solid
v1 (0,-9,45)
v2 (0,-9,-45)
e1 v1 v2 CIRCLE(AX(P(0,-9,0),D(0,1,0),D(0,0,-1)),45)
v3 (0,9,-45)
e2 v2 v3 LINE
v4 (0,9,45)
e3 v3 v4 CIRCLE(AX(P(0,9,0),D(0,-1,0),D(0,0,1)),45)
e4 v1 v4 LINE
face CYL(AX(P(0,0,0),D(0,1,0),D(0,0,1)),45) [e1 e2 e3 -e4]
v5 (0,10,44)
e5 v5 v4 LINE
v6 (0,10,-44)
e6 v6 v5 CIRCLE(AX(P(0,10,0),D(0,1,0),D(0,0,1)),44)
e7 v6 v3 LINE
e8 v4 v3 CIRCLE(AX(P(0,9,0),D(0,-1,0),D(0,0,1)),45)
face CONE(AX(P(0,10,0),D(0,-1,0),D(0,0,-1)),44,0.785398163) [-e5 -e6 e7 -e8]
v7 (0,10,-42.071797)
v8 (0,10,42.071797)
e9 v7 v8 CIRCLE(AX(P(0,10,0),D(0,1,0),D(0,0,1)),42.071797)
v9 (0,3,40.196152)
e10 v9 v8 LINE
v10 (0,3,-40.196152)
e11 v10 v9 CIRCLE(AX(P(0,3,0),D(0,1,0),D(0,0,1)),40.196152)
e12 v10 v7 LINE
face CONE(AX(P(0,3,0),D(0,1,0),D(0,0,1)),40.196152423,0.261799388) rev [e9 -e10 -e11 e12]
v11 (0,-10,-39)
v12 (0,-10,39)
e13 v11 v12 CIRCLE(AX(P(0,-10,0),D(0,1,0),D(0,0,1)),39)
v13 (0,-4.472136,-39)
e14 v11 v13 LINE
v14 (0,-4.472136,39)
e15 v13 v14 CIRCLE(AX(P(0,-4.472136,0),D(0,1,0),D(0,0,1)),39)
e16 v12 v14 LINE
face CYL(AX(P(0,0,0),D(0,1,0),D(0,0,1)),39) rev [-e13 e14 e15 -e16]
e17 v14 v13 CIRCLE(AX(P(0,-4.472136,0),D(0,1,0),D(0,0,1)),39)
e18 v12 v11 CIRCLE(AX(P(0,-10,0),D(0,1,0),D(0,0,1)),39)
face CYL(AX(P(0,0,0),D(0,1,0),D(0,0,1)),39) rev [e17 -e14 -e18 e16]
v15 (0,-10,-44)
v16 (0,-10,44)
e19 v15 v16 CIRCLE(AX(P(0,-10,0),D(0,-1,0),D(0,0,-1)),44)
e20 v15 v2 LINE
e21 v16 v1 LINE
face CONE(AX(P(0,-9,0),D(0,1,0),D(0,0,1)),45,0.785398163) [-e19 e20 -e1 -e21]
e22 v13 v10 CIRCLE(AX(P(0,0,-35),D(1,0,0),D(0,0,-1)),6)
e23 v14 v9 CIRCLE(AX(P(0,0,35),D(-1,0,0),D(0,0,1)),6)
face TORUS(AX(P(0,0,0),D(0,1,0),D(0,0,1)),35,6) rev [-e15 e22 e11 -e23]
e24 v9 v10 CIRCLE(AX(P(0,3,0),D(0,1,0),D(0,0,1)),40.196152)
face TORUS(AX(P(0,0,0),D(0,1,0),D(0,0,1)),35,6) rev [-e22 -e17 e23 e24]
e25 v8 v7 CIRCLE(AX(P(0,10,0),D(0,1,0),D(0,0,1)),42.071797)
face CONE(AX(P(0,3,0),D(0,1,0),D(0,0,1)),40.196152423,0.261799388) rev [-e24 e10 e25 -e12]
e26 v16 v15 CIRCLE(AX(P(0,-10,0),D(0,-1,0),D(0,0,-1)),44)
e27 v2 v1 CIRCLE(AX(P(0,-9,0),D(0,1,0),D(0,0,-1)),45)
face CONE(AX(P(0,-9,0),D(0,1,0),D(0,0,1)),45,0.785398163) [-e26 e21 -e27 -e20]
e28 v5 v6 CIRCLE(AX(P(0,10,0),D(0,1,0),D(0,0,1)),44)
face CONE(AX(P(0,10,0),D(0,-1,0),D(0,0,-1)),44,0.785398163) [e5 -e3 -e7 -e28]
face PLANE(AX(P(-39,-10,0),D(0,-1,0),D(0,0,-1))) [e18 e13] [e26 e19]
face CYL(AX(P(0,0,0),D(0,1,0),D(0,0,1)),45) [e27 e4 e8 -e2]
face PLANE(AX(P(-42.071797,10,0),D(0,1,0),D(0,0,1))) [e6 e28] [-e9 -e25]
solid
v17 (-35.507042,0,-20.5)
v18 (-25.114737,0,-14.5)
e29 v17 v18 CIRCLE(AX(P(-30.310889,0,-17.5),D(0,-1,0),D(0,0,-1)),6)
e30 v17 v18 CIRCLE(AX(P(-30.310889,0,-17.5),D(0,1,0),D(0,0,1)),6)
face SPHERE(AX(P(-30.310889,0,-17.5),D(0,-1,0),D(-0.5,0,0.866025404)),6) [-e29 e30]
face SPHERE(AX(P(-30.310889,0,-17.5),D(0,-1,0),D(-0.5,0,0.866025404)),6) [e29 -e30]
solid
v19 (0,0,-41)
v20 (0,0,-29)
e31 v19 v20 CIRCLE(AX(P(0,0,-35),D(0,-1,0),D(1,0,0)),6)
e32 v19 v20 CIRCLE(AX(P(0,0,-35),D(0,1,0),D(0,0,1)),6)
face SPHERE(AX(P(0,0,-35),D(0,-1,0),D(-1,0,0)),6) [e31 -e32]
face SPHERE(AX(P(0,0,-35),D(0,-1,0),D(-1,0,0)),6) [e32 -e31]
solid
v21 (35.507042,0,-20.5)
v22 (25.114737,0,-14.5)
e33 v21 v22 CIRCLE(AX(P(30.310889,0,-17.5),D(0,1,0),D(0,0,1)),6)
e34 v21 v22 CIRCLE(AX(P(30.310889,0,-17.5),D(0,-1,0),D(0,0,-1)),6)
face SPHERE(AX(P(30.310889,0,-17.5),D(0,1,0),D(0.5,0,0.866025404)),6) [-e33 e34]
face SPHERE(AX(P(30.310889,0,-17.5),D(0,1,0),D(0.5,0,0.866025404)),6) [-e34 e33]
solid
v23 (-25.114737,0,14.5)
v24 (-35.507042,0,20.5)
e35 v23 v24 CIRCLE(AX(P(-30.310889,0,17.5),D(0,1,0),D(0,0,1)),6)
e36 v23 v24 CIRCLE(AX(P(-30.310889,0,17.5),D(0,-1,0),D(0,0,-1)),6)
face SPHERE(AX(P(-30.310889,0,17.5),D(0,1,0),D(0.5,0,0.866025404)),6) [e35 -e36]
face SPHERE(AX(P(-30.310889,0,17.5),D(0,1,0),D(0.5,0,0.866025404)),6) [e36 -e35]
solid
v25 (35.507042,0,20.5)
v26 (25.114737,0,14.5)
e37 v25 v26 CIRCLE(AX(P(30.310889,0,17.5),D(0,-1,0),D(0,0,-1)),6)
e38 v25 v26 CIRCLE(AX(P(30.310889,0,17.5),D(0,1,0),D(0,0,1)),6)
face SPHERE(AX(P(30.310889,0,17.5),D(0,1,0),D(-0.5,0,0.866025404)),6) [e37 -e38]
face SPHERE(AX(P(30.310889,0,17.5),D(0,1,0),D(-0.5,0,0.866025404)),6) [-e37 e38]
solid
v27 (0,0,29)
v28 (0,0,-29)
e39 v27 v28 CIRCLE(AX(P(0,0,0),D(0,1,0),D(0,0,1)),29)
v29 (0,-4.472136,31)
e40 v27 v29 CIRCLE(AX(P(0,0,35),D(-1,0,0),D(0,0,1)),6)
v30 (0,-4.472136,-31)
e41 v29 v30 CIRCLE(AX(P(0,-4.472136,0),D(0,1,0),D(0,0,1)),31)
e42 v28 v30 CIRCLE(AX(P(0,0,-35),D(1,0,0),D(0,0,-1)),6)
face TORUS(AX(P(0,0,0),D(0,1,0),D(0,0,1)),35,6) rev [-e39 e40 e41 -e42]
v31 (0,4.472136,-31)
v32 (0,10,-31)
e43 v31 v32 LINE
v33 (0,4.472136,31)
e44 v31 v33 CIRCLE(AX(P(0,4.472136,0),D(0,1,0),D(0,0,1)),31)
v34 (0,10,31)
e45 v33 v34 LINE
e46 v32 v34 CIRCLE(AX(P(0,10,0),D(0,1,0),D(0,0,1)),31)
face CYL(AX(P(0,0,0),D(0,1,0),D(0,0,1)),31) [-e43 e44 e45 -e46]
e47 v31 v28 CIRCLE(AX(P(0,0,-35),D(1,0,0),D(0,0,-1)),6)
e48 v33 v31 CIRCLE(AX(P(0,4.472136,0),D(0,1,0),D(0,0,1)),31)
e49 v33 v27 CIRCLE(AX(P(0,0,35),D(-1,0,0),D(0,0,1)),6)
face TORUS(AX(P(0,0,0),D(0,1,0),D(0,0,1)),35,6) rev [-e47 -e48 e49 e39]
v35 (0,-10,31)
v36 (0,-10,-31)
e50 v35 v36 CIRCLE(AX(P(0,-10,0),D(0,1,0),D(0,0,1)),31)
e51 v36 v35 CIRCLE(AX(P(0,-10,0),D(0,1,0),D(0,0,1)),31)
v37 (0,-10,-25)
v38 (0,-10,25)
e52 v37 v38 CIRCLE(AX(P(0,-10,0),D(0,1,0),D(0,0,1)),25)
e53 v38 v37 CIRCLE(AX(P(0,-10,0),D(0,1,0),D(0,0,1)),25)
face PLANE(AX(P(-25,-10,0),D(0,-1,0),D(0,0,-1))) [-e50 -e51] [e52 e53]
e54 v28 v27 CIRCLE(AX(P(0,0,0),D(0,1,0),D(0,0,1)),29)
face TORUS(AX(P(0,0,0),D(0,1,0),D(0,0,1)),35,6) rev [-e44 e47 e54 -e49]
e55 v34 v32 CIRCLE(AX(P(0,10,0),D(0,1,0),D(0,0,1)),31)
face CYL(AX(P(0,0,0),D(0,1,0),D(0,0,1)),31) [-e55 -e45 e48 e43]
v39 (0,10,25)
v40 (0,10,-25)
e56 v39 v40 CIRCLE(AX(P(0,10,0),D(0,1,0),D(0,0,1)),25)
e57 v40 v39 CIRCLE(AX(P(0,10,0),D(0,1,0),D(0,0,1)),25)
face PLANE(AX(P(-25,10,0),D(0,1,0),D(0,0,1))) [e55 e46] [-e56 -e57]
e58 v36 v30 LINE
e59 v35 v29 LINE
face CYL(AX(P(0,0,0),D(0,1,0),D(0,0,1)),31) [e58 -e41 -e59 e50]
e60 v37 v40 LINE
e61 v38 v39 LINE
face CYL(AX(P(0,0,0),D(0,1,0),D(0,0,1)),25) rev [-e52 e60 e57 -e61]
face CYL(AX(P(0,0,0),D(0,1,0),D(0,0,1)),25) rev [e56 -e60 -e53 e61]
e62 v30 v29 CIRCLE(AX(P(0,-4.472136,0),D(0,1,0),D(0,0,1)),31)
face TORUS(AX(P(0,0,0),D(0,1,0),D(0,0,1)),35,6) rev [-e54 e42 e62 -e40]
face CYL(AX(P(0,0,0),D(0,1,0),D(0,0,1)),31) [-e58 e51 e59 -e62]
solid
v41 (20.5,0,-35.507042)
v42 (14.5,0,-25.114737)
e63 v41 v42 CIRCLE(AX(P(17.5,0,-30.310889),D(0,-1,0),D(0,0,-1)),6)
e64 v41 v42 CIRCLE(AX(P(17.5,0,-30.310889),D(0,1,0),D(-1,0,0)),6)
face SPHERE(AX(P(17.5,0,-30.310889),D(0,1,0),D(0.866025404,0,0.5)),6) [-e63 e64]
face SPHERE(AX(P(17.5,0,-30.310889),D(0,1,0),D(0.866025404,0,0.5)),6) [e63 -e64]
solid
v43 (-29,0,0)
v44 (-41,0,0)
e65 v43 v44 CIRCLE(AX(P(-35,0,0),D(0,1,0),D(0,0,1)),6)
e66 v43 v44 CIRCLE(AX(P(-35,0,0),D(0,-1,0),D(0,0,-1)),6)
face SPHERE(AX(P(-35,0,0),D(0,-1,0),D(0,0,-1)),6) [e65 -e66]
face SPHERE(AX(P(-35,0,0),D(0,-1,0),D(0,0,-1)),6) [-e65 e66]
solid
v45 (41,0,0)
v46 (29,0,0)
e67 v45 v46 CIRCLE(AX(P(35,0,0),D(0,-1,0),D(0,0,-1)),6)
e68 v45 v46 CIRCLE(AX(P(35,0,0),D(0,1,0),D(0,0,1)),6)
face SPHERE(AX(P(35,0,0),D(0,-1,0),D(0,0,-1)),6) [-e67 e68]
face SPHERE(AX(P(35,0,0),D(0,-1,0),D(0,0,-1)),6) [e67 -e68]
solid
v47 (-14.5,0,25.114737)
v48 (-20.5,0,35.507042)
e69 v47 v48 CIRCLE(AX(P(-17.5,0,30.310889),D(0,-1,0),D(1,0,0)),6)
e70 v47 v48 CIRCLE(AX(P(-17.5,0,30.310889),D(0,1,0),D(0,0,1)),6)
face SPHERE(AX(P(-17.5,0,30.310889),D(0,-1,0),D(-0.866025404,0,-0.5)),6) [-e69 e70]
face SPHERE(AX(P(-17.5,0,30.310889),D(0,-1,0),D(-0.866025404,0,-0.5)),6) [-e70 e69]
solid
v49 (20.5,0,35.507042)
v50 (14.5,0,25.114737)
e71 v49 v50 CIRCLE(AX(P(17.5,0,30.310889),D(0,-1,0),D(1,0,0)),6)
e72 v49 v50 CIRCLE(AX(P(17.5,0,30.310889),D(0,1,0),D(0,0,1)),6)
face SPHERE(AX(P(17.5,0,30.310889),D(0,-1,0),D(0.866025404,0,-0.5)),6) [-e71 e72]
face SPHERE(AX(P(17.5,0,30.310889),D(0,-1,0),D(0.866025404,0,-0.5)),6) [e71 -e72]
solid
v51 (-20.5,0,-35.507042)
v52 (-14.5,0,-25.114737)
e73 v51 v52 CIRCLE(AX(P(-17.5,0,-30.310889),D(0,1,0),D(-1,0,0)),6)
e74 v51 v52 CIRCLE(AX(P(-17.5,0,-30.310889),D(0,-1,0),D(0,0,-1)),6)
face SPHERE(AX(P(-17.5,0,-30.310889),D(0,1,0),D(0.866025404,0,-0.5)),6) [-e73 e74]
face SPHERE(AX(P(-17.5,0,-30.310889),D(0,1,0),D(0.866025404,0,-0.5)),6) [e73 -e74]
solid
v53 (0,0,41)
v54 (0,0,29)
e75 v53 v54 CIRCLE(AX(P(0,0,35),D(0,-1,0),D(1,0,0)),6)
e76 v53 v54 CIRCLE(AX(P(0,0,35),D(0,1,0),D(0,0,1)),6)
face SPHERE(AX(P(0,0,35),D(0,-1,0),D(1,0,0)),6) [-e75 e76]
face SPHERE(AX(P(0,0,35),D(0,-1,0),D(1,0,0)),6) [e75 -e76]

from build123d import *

# Parameters (mm, degrees)
CHAMFER1_SIZE = 1


with BuildPart() as part:
    # Sketch1 → Revolve1 (revolve)
    with BuildSketch(Plane.XY, mode=Mode.PRIVATE) as revolve1_sk:
        with BuildLine():
            Line((-25, 10), (-31, 10))
            Line((-31, 10), (-31, 4.472135955))
            ThreePointArc((-31, 4.472135955), (-29, 0), (-31, -4.472135955))
            Line((-31, -4.472135955), (-31, -10))
            Line((-31, -10), (-25, -10))
            Line((-25, -10), (-25, 10))
        make_face()
        with BuildLine():
            Line((-45, 10), (-45, -10))
            Line((-45, -10), (-39, -10))
            Line((-39, -10), (-39, -4.472135955))
            ThreePointArc((-39, -4.472135955), (-40.924568236, -0.948415111), (-40.196152423, 3))
            Line((-40.196152423, 3), (-42.07179677, 10))
            Line((-42.07179677, 10), (-45, 10))
        make_face()
    revolve(revolve1_sk.sketch.rotate(Axis((0, 0, 0), (0, -1, 0)), 270), axis=Axis((0, 0, 0), (0, -1, 0)))

    # Chamfer1
    chamfer1_edges = [part.edges().sort_by_distance(p)[0] for p in [
        (0, -10, -45),
        (0, 10, -45),
    ]]
    chamfer(chamfer1_edges, length=CHAMFER1_SIZE)


with BuildPart() as body_2:
    # Sketch2 → Revolve2 (revolve)
    with BuildSketch(Plane(origin=(0, 0, 0), x_dir=(1, 0, 0), z_dir=(0, 1, 0))):
        with BuildLine():
            Line((0, 29), (0, 41))
            ThreePointArc((0, 41), (6, 35), (0, 29))
        make_face()
    revolve(axis=Axis((0, 0, -29), (0, 0, -1)))


with BuildPart() as body_3:
    # Sketch3 → Revolve3 (revolve)
    with BuildSketch(Plane(origin=(0, 0, 0), x_dir=(1, 0, 0), z_dir=(0, 1, 0))):
        with BuildLine():
            Line((-14.5, 25.11473671), (-20.5, 35.507041555))
            ThreePointArc((-20.5, 35.507041555), (-12.303847577, 33.310889132), (-14.5, 25.11473671))
        make_face()
    revolve(axis=Axis((-14.5, 0, -25.11473671), (-0.5000000000000014, 0, -0.8660254037844379)))


with BuildPart() as body_4:
    # Sketch4 → Revolve4 (revolve)
    with BuildSketch(Plane(origin=(0, 0, 0), x_dir=(1, 0, 0), z_dir=(0, 1, 0))):
        with BuildLine():
            Line((-25.11473671, 14.5), (-35.507041555, 20.5))
            ThreePointArc((-35.507041555, 20.5), (-27.310889132, 22.696152423), (-25.11473671, 14.5))
        make_face()
    revolve(axis=Axis((-25.11473671, 0, -14.5), (-0.8660254037844399, 0, -0.49999999999999784)))


with BuildPart() as body_5:
    # Sketch6 → Revolve6 (revolve)
    with BuildSketch(Plane(origin=(0, 0, 0), x_dir=(1, 0, 0), z_dir=(0, 1, 0))):
        with BuildLine():
            Line((-35.507041555, -20.5), (-25.11473671, -14.5))
            ThreePointArc((-25.11473671, -14.5), (-33.310889132, -12.303847577), (-35.507041555, -20.5))
        make_face()
    revolve(axis=Axis((-35.507041555, 0, 20.5), (0.866025403784436, 0, -0.5000000000000047)))


with BuildPart() as body_6:
    # Sketch7 → Revolve7 (revolve)
    with BuildSketch(Plane(origin=(0, 0, 0), x_dir=(1, 0, 0), z_dir=(0, 1, 0))):
        with BuildLine():
            Line((-20.5, -35.507041555), (-14.5, -25.11473671))
            ThreePointArc((-14.5, -25.11473671), (-22.696152423, -27.310889132), (-20.5, -35.507041555))
        make_face()
    revolve(axis=Axis((-20.5, 0, 35.507041555), (0.4999999999999949, 0, -0.8660254037844416)))


with BuildPart() as body_7:
    # Sketch8 → Revolve8 (revolve)
    with BuildSketch(Plane(origin=(0, 0, 0), x_dir=(1, 0, 0), z_dir=(0, 1, 0))):
        with BuildLine():
            Line((0, -29), (0, -41))
            ThreePointArc((0, -41), (-6, -35), (0, -29))
        make_face()
    revolve(axis=Axis((0, 0, 29), (0, 0, 1)))


with BuildPart() as body_8:
    # Sketch9 → Revolve9 (revolve)
    with BuildSketch(Plane(origin=(0, 0, 0), x_dir=(1, 0, 0), z_dir=(0, 1, 0))):
        with BuildLine():
            Line((14.5, 25.11473671), (20.5, 35.507041555))
            ThreePointArc((20.5, 35.507041555), (12.303847577, 33.310889132), (14.5, 25.11473671))
        make_face()
    revolve(axis=Axis((14.5, 0, -25.11473671), (0.5000000000000011, 0, -0.866025403784438)))


with BuildPart() as body_9:
    # Sketch10 → Revolve10 (revolve)
    with BuildSketch(Plane(origin=(0, 0, 0), x_dir=(1, 0, 0), z_dir=(0, 1, 0))):
        with BuildLine():
            Line((25.11473671, 14.5), (35.507041555, 20.5))
            ThreePointArc((35.507041555, 20.5), (27.310889132, 22.696152423), (25.11473671, 14.5))
        make_face()
    revolve(axis=Axis((25.11473671, 0, -14.5), (0.8660254037844397, 0, -0.4999999999999981)))


with BuildPart() as body_10:
    # Sketch11 → Revolve11 (revolve)
    with BuildSketch(Plane(origin=(0, 0, 0), x_dir=(1, 0, 0), z_dir=(0, 1, 0))):
        with BuildLine():
            Line((29, 0), (41, 0))
            ThreePointArc((41, 0), (35, 6), (29, 0))
        make_face()
    revolve(axis=Axis((29, 0, 0), (1, 0, 0)))


with BuildPart() as body_11:
    # Sketch12 → Revolve12 (revolve)
    with BuildSketch(Plane(origin=(0, 0, 0), x_dir=(1, 0, 0), z_dir=(0, 1, 0))):
        with BuildLine():
            Line((25.11473671, -14.5), (35.507041555, -20.5))
            ThreePointArc((35.507041555, -20.5), (33.310889132, -12.303847577), (25.11473671, -14.5))
        make_face()
    revolve(axis=Axis((25.11473671, 0, 14.5), (0.8660254037844363, 0, 0.5000000000000043)))


with BuildPart() as body_12:
    # Sketch13 → Revolve13 (revolve)
    with BuildSketch(Plane(origin=(0, 0, 0), x_dir=(1, 0, 0), z_dir=(0, 1, 0))):
        with BuildLine():
            Line((14.5, -25.11473671), (20.5, -35.507041555))
            ThreePointArc((20.5, -35.507041555), (22.696152423, -27.310889132), (14.5, -25.11473671))
        make_face()
    revolve(axis=Axis((14.5, 0, 25.11473671), (0.49999999999999484, 0, 0.8660254037844417)))


with BuildPart() as body_13:
    # Sketch14 → Revolve14 (revolve)
    with BuildSketch(Plane(origin=(0, 0, 0), x_dir=(1, 0, 0), z_dir=(0, 1, 0))):
        with BuildLine():
            Line((-41, 0), (-29, 0))
            ThreePointArc((-29, 0), (-35, 6), (-41, 0))
        make_face()
    revolve(axis=Axis((-41, 0, 0), (1, 0, 0)))


solid = Compound([part.part, body_2.part, body_3.part, body_4.part, body_5.part, body_6.part, body_7.part, body_8.part, body_9.part, body_10.part, body_11.part, body_12.part, body_13.part])
